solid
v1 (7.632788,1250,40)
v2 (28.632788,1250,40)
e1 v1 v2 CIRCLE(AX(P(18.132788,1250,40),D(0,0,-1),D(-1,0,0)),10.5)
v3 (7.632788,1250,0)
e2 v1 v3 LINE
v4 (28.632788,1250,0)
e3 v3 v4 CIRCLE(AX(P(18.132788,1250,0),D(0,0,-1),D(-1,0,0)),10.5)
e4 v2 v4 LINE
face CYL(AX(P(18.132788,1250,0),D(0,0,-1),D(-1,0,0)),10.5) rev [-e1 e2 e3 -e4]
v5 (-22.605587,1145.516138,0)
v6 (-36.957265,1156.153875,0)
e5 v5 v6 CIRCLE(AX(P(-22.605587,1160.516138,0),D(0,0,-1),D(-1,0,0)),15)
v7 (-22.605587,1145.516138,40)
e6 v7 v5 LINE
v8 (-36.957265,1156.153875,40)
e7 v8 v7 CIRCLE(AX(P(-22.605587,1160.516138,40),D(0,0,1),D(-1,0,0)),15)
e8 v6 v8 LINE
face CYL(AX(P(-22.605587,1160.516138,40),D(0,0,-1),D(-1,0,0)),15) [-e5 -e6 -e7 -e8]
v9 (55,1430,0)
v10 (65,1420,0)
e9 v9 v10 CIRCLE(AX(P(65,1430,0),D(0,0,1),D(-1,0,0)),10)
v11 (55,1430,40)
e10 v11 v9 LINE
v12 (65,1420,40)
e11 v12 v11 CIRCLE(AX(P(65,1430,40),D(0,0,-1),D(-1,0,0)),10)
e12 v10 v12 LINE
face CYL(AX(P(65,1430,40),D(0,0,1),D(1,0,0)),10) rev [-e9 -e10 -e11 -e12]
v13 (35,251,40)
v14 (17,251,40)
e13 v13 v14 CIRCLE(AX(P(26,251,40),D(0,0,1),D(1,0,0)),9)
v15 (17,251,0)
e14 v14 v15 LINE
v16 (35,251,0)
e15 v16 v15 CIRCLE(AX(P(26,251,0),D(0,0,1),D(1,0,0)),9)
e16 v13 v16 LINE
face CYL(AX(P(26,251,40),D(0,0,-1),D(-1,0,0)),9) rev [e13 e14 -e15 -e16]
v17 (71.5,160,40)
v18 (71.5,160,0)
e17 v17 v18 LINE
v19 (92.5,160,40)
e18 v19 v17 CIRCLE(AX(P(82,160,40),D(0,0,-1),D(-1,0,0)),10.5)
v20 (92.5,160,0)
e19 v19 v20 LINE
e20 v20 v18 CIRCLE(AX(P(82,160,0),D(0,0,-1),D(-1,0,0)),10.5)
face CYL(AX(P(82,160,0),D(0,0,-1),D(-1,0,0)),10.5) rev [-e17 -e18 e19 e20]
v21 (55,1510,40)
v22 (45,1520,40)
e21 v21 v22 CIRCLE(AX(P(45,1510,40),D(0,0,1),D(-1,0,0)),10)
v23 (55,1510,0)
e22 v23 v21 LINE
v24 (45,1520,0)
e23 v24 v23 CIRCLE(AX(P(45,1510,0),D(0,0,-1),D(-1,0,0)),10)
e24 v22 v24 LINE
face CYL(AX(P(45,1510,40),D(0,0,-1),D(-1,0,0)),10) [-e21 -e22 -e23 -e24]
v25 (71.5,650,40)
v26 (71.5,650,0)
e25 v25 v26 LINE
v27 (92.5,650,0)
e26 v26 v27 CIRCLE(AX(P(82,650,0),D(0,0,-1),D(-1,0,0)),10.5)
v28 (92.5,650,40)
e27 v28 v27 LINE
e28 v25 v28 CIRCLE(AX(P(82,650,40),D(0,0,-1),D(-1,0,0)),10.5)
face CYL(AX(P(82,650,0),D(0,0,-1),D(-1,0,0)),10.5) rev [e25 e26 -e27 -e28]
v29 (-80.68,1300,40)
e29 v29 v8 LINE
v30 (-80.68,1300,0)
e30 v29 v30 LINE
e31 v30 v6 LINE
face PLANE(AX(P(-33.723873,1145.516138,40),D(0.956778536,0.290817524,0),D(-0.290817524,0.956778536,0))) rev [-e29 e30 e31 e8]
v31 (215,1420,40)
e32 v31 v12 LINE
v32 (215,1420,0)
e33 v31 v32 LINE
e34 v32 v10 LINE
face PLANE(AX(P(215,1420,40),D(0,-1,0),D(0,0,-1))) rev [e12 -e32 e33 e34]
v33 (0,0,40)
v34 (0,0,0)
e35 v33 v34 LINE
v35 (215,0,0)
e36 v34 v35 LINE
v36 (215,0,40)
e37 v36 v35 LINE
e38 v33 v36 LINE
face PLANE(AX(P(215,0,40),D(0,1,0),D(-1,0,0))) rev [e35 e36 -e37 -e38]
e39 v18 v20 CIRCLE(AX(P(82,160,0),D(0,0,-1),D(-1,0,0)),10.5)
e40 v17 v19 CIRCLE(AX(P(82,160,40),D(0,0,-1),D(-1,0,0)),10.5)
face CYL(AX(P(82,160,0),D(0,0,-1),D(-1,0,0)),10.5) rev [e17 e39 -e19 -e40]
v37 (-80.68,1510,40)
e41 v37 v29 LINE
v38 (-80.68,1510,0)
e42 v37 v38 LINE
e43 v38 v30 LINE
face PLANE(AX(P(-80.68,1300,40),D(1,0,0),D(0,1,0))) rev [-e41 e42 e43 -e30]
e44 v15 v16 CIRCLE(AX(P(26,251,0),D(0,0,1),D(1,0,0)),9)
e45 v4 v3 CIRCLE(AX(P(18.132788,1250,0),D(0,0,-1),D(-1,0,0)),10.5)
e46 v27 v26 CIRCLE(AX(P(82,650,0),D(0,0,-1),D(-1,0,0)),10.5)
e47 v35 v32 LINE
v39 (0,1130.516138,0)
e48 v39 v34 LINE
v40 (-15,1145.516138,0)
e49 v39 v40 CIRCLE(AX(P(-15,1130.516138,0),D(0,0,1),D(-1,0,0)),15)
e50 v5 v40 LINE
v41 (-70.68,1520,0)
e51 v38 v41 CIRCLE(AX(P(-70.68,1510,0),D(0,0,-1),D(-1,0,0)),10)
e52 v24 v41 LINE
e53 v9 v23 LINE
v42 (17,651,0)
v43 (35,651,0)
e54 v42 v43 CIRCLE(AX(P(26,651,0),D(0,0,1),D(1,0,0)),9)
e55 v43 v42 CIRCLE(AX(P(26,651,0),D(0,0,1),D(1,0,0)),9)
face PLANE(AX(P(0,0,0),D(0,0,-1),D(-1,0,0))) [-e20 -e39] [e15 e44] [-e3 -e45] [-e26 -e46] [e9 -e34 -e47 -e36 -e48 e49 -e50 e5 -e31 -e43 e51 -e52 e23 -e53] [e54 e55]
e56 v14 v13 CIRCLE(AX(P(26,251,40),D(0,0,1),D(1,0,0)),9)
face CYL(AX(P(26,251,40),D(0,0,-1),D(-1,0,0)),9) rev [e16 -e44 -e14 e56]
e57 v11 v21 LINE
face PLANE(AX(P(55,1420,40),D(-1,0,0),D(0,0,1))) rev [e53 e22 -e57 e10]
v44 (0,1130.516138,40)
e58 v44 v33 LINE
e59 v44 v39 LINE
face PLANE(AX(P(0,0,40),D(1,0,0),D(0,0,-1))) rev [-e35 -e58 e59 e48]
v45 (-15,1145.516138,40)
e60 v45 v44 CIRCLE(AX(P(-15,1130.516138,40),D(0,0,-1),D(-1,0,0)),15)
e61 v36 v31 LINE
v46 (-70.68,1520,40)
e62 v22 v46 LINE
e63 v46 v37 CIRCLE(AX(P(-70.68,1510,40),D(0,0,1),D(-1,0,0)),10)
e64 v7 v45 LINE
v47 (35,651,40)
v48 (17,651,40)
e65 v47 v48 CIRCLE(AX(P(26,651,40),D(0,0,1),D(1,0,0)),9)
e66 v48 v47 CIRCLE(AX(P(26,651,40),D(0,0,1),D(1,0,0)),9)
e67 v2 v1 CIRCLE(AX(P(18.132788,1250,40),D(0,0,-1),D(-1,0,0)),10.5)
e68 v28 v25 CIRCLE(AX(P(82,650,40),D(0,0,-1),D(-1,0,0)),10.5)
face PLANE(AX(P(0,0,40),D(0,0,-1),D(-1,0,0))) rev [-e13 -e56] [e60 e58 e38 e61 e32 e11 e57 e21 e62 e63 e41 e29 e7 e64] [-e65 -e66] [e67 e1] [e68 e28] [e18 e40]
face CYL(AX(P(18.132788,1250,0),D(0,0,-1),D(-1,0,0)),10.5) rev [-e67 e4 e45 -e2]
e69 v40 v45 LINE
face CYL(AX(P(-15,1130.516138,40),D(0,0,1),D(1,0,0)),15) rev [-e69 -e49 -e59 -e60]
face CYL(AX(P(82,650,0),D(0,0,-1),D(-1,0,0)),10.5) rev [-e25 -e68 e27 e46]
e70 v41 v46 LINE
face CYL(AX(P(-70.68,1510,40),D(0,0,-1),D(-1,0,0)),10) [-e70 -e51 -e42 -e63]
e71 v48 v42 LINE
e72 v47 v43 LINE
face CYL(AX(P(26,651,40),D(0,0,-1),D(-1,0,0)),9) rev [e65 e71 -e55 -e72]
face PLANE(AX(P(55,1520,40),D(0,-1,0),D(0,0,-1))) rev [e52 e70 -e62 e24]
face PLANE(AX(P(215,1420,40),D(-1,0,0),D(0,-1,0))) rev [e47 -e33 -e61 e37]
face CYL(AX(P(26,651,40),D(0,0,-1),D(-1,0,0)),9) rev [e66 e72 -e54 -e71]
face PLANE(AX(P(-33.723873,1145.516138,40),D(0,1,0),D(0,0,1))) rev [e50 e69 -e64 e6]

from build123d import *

# Parameters (mm, degrees)
SKETCH1_R           = 9
BOSS_EXTRUDE1_DEPTH = 40
M24_TAPPED_HOLE1_D  = 21
FILLET1_R           = 15
FILLET2_R           = 10


with BuildPart() as part:
    # Sketch1 → Boss-Extrude1 (new body)
    with BuildSketch(Plane.XY):
        Polygon((0, 0), (0, 1145.516137583), (-33.72387302, 1145.516137583), (-80.68, 1300), (-80.68, 1520), (55, 1520), (55, 1420), (215, 1420), (215, 0), align=None)
        with Locations((26, 251)):
            Circle(SKETCH1_R, mode=Mode.SUBTRACT)
        with Locations((26, 651)):
            Circle(SKETCH1_R, mode=Mode.SUBTRACT)
    extrude(amount=BOSS_EXTRUDE1_DEPTH)

    # M24 Tapped Hole1 (through all)
    with Locations(Plane(origin=(18.132788177, 1250, 0), x_dir=(-1, 0, 0), z_dir=(0, 0, -1))):
        with Locations((0, 0), (-63.867211823, -600), (-63.867211823, -1090)):
            Hole(M24_TAPPED_HOLE1_D / 2)

    # Fillet1
    fillet1_edges = [part.edges().sort_by_distance(p)[0] for p in [
        (0, 1145.516137583, 20),
        (-33.72387302, 1145.516137583, 20),
    ]]
    fillet(fillet1_edges, radius=FILLET1_R)

    # Fillet2
    fillet2_edges = [part.edges().sort_by_distance(p)[0] for p in [
        (-80.68, 1520, 20),
        (55, 1520, 20),
        (55, 1420, 20),
    ]]
    fillet(fillet2_edges, radius=FILLET2_R)


solid = part.part
